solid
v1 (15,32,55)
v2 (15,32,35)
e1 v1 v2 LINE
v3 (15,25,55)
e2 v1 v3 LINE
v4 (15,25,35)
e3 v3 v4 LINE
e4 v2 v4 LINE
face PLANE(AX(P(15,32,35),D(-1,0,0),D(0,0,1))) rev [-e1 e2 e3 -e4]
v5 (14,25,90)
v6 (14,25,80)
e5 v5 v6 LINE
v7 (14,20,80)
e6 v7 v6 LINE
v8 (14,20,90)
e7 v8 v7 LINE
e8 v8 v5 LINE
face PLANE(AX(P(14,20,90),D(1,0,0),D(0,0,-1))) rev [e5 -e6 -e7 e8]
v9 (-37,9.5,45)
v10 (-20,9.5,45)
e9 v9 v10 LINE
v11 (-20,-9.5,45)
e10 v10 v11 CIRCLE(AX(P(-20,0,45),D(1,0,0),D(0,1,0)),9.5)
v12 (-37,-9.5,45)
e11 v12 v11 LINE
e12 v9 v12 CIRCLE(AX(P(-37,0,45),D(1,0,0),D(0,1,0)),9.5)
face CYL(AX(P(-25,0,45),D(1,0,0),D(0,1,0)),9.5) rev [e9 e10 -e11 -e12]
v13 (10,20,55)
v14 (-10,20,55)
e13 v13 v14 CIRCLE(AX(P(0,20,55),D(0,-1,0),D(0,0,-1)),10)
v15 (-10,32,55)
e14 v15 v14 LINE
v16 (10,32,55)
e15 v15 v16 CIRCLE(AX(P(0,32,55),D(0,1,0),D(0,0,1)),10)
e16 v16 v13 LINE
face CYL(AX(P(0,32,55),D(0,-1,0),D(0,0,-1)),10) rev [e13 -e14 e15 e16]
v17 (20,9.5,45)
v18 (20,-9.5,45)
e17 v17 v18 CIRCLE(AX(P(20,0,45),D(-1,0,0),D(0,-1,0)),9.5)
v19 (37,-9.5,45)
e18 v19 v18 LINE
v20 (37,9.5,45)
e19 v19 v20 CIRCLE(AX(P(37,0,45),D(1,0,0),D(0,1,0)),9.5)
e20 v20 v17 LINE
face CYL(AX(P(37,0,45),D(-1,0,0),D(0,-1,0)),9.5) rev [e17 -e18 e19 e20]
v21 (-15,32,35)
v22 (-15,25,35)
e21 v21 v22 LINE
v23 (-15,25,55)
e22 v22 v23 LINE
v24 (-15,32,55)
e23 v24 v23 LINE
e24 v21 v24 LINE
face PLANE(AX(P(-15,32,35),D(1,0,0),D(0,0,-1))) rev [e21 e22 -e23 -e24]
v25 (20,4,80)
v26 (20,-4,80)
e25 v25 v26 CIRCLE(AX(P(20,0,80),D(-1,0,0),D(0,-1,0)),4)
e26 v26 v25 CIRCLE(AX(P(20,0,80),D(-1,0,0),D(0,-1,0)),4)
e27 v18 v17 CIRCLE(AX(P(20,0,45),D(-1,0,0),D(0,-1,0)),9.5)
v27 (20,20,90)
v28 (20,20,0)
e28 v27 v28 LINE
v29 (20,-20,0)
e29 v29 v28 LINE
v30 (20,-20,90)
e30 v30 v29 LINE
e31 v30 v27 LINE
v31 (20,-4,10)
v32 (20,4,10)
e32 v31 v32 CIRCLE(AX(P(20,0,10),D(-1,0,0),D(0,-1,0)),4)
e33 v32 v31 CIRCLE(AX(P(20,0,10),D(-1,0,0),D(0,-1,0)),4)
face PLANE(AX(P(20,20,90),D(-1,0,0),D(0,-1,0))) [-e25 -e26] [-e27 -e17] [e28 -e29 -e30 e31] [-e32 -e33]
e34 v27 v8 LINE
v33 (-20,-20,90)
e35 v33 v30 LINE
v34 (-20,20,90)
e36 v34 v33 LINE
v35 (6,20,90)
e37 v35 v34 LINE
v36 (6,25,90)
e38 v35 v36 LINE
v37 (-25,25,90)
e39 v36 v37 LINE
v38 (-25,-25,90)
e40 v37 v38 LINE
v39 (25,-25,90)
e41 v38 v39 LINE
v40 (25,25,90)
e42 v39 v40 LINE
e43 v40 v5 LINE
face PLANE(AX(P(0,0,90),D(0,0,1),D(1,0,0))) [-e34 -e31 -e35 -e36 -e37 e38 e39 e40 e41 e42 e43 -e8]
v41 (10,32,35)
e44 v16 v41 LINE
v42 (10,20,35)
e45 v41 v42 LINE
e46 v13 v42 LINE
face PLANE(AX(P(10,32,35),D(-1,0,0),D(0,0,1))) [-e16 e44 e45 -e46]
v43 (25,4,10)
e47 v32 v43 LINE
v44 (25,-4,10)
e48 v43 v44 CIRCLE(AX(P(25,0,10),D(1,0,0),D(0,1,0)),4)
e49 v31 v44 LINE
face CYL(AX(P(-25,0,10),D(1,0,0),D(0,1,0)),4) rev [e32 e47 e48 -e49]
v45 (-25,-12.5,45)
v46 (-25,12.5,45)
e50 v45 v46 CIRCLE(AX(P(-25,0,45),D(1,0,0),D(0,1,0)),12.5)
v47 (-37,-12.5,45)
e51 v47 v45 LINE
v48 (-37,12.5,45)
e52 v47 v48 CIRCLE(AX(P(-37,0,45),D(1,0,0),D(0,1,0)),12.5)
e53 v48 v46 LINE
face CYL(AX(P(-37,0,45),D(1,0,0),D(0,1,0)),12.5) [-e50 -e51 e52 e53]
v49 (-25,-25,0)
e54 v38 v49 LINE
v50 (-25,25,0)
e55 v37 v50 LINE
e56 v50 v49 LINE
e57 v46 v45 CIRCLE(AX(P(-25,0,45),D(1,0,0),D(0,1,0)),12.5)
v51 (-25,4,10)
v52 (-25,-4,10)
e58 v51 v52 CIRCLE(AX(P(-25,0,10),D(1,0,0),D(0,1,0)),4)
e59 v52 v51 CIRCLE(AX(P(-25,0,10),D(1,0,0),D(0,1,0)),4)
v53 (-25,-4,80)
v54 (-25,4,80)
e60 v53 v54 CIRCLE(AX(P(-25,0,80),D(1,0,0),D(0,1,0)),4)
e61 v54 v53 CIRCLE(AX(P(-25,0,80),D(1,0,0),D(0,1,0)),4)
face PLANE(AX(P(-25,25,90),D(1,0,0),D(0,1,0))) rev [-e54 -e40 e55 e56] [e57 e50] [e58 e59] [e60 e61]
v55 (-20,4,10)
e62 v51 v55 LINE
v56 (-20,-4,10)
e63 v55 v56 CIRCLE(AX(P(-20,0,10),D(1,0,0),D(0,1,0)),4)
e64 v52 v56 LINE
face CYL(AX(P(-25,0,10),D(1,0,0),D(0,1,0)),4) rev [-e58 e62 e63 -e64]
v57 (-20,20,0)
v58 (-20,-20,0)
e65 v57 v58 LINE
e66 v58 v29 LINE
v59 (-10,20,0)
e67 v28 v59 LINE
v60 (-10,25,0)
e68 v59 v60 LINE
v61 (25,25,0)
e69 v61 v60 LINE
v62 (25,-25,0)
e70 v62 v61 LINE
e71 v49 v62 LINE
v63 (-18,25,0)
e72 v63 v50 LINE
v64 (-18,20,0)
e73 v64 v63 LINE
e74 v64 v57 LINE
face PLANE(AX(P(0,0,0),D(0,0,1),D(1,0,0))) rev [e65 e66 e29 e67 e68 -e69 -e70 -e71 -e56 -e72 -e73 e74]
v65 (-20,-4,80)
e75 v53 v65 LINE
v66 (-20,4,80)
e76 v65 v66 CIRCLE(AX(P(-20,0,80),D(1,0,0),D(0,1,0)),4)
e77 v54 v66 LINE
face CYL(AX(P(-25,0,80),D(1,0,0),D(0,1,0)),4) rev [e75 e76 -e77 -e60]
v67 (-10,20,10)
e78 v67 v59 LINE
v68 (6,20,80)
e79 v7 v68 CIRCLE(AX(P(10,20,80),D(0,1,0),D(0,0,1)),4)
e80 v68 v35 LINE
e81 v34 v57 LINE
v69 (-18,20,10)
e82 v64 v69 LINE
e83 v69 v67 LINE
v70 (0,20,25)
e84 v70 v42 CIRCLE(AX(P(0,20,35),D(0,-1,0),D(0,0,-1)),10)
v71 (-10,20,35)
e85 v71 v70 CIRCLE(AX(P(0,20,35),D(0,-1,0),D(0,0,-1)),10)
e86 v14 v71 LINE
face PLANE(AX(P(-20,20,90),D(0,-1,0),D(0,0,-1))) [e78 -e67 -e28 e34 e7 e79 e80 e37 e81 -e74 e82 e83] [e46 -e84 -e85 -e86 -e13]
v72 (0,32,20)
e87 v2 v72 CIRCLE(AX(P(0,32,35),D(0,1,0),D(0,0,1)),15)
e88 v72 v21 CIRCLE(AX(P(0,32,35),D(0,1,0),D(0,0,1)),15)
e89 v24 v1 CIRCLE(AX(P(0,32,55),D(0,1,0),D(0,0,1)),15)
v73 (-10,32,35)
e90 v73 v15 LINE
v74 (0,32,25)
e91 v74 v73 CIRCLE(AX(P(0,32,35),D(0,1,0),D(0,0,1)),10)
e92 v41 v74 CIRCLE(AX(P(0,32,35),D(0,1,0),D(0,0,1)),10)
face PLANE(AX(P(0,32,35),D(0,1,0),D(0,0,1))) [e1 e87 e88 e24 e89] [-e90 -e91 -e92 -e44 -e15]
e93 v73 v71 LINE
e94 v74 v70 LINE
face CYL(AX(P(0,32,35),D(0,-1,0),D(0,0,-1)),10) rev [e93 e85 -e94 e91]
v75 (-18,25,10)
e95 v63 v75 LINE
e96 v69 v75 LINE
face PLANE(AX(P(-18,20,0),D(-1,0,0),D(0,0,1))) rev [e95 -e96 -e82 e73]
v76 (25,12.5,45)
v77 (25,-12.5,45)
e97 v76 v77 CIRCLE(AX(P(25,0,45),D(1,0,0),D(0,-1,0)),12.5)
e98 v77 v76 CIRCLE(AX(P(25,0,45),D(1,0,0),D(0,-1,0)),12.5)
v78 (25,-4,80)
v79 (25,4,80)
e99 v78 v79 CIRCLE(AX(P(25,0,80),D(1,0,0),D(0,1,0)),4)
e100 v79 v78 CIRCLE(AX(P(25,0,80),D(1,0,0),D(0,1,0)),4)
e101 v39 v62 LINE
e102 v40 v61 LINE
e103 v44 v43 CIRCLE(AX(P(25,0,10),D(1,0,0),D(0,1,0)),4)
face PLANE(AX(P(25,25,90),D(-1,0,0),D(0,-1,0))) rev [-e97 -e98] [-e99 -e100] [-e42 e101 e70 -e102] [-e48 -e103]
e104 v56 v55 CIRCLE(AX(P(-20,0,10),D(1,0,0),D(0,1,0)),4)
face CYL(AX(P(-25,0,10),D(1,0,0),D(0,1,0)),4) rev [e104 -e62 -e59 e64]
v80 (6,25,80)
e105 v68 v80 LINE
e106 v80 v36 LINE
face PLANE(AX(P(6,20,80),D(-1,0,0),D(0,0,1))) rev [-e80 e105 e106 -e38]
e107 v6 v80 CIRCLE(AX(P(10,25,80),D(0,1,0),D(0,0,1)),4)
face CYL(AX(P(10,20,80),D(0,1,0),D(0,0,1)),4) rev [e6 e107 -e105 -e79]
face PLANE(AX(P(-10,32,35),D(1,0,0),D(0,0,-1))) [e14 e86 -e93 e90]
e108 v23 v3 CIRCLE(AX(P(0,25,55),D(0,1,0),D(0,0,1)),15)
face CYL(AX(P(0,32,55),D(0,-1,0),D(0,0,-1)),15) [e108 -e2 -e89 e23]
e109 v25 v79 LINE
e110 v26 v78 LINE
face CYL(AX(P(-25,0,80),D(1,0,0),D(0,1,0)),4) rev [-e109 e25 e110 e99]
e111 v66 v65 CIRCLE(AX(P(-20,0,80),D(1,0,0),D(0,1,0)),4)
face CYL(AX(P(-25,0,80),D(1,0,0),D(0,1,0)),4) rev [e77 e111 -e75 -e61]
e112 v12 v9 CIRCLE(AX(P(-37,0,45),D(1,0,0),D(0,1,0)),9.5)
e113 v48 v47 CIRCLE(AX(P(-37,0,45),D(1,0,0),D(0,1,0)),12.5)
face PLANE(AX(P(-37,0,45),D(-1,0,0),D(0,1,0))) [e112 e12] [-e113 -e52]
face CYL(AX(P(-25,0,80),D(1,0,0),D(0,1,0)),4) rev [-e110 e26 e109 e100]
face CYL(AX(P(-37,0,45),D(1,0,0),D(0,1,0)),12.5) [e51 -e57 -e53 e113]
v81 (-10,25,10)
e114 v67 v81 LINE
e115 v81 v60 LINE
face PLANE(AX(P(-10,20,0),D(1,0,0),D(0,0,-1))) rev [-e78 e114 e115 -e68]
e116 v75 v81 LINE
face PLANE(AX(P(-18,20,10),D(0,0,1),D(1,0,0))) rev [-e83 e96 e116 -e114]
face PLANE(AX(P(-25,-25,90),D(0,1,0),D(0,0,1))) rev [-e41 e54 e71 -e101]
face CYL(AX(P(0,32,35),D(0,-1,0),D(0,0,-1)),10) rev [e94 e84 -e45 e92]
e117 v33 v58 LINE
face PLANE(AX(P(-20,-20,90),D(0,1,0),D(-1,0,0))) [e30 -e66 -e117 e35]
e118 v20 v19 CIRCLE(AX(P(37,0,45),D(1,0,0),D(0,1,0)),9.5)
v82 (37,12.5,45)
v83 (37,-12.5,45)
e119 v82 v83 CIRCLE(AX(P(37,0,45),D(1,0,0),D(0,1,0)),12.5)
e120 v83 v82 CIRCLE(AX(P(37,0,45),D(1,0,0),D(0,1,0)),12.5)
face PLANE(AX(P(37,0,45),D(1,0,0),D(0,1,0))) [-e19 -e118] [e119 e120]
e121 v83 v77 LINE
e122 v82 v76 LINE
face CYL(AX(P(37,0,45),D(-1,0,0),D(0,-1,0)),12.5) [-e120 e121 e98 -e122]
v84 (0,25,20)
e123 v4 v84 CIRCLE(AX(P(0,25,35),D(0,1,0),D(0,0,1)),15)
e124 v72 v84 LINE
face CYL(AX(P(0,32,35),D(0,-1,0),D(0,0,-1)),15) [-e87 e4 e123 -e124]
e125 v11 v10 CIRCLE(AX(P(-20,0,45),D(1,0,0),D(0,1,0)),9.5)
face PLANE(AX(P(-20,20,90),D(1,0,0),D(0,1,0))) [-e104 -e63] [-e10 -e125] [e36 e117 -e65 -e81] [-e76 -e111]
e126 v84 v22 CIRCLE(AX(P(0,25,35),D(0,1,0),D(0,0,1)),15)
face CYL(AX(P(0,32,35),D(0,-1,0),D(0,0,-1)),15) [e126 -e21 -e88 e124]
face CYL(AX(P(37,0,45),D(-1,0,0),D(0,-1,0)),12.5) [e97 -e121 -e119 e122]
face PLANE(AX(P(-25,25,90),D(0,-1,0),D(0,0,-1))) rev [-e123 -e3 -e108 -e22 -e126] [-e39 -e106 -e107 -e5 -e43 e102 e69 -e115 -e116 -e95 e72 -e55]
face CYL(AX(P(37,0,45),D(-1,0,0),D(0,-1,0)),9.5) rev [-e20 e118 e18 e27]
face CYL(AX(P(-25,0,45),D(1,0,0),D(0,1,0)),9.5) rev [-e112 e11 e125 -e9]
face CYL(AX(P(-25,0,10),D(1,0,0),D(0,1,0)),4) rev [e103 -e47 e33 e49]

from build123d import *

# Parameters (mm, degrees)
TUBE_PROFILE_50X50X5_SKETCH_W   = 50
TUBE_PROFILE_50X50X5_SKETCH_H   = 50
TUBE_PROFILE_50X50X5_SKETCH_W_2 = 40
TUBE_PROFILE_50X50X5_SKETCH_H_2 = 40
SQUARE_TUBE_BODY_L90_DEPTH      = 90
KEYHOLE_NOTCH_SKETCH_W          = 8
KEYHOLE_NOTCH_SKETCH_H          = 10
KEYHOLE_NOTCHES_DEPTH           = 5
OBROUND_BOSS_DEPTH              = 7
OBROUND_START                   = -7
OBROUND_SLOT_CUT_DEPTH          = 7
SIDE_BOSS_AND_HOLES_SKETCH_R    = 12.5
SIDE_BOSS_AND_HOLES_SKETCH_R_2  = 9.5
SIDE_BOSS_25_DEPTH              = 12
SKETCH7_3_R                     = 4
SKETCH7_3_R_2                   = 9.5
SIDE_BORE_AND_HOLES_DEPTH       = 108.814655776


with BuildPart() as part:
    # Tube Profile 50x50x5 Sketch → Square Tube Body L90 (new body)
    with BuildSketch(Plane.XY):
        Rectangle(TUBE_PROFILE_50X50X5_SKETCH_W, TUBE_PROFILE_50X50X5_SKETCH_H)
        Rectangle(TUBE_PROFILE_50X50X5_SKETCH_W_2, TUBE_PROFILE_50X50X5_SKETCH_H_2, mode=Mode.SUBTRACT)
    extrude(amount=SQUARE_TUBE_BODY_L90_DEPTH)

    # Keyhole Notch Sketch → Keyhole Notches (cut)
    with BuildSketch(Plane(origin=(0, 25, 0), x_dir=(1, 0, 0), z_dir=(0, 1, 0))):
        with BuildLine():
            Line((14, -90), (14, -80))
            ThreePointArc((14, -80), (10, -76), (6, -80))
            Line((6, -80), (6, -90))
            Line((6, -90), (14, -90))
        make_face()
        with Locations((-14, -5)):
            Rectangle(KEYHOLE_NOTCH_SKETCH_W, KEYHOLE_NOTCH_SKETCH_H)
    extrude(amount=-KEYHOLE_NOTCHES_DEPTH, mode=Mode.SUBTRACT)

    # Obround Boss Sketch → Obround Boss (add)
    with BuildSketch(Plane(origin=(0, 25, 0), x_dir=(1, 0, 0), z_dir=(0, 1, 0))):
        with BuildLine():
            Line((15, -35), (15, -55))
            ThreePointArc((15, -55), (0, -70), (-15, -55))
            Line((-15, -55), (-15, -35))
            ThreePointArc((-15, -35), (0, -20), (15, -35))
        make_face()
        with BuildLine():
            Line((10, -35), (10, -55))
            ThreePointArc((10, -55), (0, -65), (-10, -55))
            Line((-10, -55), (-10, -35))
            ThreePointArc((-10, -35), (0, -25), (10, -35))
        make_face(mode=Mode.SUBTRACT)
    extrude(amount=OBROUND_BOSS_DEPTH)

    # Sketch6_2 → Obround Slot Cut (cut)
    with BuildSketch(Plane(origin=(0, 25, 0), x_dir=(1, 0, 0), z_dir=(0, 1, 0)).offset(OBROUND_START)):
        with BuildLine():
            Line((10, -35), (10, -55))
            ThreePointArc((10, -55), (0, -65), (-10, -55))
            Line((-10, -55), (-10, -35))
            ThreePointArc((-10, -35), (0, -25), (10, -35))
        make_face()
    extrude(amount=OBROUND_SLOT_CUT_DEPTH, mode=Mode.SUBTRACT)

    # Side Boss and Holes Sketch → Side Boss _25 (add)
    with BuildSketch(Plane(origin=(25, 0, 0), x_dir=(0, 0, -1), z_dir=(1, 0, 0))):
        with Locations(Location((-45, 0, 0), (0, 0, 270))):
            Circle(SIDE_BOSS_AND_HOLES_SKETCH_R)
        with Locations(Location((-45, 0, 0), (0, 0, 90))):
            Circle(SIDE_BOSS_AND_HOLES_SKETCH_R_2, mode=Mode.SUBTRACT)
    side_boss_25 = extrude(amount=SIDE_BOSS_25_DEPTH)

    # Sketch7_3 → Side Bore and Holes (cut, through all)
    with BuildSketch(Plane(origin=(25, 0, 0), x_dir=(0, 0, -1), z_dir=(1, 0, 0))):
        with Locations(Location((-80, 0, 0), (0, 0, 90))):
            Circle(SKETCH7_3_R)
        with Locations(Location((-10, 0, 0), (0, 0, 90))):
            Circle(SKETCH7_3_R)
        with Locations(Location((-45, 0, 0), (0, 0, 270))):
            Circle(SKETCH7_3_R_2)
    extrude(amount=-SIDE_BORE_AND_HOLES_DEPTH, mode=Mode.SUBTRACT)

    # Side Boss Mirror: Side Boss _25 across plane
    add(side_boss_25.mirror(Plane(origin=(0, 0, 0), x_dir=(0, 0, 1), z_dir=(1, 0, 0))))


solid = part.part
